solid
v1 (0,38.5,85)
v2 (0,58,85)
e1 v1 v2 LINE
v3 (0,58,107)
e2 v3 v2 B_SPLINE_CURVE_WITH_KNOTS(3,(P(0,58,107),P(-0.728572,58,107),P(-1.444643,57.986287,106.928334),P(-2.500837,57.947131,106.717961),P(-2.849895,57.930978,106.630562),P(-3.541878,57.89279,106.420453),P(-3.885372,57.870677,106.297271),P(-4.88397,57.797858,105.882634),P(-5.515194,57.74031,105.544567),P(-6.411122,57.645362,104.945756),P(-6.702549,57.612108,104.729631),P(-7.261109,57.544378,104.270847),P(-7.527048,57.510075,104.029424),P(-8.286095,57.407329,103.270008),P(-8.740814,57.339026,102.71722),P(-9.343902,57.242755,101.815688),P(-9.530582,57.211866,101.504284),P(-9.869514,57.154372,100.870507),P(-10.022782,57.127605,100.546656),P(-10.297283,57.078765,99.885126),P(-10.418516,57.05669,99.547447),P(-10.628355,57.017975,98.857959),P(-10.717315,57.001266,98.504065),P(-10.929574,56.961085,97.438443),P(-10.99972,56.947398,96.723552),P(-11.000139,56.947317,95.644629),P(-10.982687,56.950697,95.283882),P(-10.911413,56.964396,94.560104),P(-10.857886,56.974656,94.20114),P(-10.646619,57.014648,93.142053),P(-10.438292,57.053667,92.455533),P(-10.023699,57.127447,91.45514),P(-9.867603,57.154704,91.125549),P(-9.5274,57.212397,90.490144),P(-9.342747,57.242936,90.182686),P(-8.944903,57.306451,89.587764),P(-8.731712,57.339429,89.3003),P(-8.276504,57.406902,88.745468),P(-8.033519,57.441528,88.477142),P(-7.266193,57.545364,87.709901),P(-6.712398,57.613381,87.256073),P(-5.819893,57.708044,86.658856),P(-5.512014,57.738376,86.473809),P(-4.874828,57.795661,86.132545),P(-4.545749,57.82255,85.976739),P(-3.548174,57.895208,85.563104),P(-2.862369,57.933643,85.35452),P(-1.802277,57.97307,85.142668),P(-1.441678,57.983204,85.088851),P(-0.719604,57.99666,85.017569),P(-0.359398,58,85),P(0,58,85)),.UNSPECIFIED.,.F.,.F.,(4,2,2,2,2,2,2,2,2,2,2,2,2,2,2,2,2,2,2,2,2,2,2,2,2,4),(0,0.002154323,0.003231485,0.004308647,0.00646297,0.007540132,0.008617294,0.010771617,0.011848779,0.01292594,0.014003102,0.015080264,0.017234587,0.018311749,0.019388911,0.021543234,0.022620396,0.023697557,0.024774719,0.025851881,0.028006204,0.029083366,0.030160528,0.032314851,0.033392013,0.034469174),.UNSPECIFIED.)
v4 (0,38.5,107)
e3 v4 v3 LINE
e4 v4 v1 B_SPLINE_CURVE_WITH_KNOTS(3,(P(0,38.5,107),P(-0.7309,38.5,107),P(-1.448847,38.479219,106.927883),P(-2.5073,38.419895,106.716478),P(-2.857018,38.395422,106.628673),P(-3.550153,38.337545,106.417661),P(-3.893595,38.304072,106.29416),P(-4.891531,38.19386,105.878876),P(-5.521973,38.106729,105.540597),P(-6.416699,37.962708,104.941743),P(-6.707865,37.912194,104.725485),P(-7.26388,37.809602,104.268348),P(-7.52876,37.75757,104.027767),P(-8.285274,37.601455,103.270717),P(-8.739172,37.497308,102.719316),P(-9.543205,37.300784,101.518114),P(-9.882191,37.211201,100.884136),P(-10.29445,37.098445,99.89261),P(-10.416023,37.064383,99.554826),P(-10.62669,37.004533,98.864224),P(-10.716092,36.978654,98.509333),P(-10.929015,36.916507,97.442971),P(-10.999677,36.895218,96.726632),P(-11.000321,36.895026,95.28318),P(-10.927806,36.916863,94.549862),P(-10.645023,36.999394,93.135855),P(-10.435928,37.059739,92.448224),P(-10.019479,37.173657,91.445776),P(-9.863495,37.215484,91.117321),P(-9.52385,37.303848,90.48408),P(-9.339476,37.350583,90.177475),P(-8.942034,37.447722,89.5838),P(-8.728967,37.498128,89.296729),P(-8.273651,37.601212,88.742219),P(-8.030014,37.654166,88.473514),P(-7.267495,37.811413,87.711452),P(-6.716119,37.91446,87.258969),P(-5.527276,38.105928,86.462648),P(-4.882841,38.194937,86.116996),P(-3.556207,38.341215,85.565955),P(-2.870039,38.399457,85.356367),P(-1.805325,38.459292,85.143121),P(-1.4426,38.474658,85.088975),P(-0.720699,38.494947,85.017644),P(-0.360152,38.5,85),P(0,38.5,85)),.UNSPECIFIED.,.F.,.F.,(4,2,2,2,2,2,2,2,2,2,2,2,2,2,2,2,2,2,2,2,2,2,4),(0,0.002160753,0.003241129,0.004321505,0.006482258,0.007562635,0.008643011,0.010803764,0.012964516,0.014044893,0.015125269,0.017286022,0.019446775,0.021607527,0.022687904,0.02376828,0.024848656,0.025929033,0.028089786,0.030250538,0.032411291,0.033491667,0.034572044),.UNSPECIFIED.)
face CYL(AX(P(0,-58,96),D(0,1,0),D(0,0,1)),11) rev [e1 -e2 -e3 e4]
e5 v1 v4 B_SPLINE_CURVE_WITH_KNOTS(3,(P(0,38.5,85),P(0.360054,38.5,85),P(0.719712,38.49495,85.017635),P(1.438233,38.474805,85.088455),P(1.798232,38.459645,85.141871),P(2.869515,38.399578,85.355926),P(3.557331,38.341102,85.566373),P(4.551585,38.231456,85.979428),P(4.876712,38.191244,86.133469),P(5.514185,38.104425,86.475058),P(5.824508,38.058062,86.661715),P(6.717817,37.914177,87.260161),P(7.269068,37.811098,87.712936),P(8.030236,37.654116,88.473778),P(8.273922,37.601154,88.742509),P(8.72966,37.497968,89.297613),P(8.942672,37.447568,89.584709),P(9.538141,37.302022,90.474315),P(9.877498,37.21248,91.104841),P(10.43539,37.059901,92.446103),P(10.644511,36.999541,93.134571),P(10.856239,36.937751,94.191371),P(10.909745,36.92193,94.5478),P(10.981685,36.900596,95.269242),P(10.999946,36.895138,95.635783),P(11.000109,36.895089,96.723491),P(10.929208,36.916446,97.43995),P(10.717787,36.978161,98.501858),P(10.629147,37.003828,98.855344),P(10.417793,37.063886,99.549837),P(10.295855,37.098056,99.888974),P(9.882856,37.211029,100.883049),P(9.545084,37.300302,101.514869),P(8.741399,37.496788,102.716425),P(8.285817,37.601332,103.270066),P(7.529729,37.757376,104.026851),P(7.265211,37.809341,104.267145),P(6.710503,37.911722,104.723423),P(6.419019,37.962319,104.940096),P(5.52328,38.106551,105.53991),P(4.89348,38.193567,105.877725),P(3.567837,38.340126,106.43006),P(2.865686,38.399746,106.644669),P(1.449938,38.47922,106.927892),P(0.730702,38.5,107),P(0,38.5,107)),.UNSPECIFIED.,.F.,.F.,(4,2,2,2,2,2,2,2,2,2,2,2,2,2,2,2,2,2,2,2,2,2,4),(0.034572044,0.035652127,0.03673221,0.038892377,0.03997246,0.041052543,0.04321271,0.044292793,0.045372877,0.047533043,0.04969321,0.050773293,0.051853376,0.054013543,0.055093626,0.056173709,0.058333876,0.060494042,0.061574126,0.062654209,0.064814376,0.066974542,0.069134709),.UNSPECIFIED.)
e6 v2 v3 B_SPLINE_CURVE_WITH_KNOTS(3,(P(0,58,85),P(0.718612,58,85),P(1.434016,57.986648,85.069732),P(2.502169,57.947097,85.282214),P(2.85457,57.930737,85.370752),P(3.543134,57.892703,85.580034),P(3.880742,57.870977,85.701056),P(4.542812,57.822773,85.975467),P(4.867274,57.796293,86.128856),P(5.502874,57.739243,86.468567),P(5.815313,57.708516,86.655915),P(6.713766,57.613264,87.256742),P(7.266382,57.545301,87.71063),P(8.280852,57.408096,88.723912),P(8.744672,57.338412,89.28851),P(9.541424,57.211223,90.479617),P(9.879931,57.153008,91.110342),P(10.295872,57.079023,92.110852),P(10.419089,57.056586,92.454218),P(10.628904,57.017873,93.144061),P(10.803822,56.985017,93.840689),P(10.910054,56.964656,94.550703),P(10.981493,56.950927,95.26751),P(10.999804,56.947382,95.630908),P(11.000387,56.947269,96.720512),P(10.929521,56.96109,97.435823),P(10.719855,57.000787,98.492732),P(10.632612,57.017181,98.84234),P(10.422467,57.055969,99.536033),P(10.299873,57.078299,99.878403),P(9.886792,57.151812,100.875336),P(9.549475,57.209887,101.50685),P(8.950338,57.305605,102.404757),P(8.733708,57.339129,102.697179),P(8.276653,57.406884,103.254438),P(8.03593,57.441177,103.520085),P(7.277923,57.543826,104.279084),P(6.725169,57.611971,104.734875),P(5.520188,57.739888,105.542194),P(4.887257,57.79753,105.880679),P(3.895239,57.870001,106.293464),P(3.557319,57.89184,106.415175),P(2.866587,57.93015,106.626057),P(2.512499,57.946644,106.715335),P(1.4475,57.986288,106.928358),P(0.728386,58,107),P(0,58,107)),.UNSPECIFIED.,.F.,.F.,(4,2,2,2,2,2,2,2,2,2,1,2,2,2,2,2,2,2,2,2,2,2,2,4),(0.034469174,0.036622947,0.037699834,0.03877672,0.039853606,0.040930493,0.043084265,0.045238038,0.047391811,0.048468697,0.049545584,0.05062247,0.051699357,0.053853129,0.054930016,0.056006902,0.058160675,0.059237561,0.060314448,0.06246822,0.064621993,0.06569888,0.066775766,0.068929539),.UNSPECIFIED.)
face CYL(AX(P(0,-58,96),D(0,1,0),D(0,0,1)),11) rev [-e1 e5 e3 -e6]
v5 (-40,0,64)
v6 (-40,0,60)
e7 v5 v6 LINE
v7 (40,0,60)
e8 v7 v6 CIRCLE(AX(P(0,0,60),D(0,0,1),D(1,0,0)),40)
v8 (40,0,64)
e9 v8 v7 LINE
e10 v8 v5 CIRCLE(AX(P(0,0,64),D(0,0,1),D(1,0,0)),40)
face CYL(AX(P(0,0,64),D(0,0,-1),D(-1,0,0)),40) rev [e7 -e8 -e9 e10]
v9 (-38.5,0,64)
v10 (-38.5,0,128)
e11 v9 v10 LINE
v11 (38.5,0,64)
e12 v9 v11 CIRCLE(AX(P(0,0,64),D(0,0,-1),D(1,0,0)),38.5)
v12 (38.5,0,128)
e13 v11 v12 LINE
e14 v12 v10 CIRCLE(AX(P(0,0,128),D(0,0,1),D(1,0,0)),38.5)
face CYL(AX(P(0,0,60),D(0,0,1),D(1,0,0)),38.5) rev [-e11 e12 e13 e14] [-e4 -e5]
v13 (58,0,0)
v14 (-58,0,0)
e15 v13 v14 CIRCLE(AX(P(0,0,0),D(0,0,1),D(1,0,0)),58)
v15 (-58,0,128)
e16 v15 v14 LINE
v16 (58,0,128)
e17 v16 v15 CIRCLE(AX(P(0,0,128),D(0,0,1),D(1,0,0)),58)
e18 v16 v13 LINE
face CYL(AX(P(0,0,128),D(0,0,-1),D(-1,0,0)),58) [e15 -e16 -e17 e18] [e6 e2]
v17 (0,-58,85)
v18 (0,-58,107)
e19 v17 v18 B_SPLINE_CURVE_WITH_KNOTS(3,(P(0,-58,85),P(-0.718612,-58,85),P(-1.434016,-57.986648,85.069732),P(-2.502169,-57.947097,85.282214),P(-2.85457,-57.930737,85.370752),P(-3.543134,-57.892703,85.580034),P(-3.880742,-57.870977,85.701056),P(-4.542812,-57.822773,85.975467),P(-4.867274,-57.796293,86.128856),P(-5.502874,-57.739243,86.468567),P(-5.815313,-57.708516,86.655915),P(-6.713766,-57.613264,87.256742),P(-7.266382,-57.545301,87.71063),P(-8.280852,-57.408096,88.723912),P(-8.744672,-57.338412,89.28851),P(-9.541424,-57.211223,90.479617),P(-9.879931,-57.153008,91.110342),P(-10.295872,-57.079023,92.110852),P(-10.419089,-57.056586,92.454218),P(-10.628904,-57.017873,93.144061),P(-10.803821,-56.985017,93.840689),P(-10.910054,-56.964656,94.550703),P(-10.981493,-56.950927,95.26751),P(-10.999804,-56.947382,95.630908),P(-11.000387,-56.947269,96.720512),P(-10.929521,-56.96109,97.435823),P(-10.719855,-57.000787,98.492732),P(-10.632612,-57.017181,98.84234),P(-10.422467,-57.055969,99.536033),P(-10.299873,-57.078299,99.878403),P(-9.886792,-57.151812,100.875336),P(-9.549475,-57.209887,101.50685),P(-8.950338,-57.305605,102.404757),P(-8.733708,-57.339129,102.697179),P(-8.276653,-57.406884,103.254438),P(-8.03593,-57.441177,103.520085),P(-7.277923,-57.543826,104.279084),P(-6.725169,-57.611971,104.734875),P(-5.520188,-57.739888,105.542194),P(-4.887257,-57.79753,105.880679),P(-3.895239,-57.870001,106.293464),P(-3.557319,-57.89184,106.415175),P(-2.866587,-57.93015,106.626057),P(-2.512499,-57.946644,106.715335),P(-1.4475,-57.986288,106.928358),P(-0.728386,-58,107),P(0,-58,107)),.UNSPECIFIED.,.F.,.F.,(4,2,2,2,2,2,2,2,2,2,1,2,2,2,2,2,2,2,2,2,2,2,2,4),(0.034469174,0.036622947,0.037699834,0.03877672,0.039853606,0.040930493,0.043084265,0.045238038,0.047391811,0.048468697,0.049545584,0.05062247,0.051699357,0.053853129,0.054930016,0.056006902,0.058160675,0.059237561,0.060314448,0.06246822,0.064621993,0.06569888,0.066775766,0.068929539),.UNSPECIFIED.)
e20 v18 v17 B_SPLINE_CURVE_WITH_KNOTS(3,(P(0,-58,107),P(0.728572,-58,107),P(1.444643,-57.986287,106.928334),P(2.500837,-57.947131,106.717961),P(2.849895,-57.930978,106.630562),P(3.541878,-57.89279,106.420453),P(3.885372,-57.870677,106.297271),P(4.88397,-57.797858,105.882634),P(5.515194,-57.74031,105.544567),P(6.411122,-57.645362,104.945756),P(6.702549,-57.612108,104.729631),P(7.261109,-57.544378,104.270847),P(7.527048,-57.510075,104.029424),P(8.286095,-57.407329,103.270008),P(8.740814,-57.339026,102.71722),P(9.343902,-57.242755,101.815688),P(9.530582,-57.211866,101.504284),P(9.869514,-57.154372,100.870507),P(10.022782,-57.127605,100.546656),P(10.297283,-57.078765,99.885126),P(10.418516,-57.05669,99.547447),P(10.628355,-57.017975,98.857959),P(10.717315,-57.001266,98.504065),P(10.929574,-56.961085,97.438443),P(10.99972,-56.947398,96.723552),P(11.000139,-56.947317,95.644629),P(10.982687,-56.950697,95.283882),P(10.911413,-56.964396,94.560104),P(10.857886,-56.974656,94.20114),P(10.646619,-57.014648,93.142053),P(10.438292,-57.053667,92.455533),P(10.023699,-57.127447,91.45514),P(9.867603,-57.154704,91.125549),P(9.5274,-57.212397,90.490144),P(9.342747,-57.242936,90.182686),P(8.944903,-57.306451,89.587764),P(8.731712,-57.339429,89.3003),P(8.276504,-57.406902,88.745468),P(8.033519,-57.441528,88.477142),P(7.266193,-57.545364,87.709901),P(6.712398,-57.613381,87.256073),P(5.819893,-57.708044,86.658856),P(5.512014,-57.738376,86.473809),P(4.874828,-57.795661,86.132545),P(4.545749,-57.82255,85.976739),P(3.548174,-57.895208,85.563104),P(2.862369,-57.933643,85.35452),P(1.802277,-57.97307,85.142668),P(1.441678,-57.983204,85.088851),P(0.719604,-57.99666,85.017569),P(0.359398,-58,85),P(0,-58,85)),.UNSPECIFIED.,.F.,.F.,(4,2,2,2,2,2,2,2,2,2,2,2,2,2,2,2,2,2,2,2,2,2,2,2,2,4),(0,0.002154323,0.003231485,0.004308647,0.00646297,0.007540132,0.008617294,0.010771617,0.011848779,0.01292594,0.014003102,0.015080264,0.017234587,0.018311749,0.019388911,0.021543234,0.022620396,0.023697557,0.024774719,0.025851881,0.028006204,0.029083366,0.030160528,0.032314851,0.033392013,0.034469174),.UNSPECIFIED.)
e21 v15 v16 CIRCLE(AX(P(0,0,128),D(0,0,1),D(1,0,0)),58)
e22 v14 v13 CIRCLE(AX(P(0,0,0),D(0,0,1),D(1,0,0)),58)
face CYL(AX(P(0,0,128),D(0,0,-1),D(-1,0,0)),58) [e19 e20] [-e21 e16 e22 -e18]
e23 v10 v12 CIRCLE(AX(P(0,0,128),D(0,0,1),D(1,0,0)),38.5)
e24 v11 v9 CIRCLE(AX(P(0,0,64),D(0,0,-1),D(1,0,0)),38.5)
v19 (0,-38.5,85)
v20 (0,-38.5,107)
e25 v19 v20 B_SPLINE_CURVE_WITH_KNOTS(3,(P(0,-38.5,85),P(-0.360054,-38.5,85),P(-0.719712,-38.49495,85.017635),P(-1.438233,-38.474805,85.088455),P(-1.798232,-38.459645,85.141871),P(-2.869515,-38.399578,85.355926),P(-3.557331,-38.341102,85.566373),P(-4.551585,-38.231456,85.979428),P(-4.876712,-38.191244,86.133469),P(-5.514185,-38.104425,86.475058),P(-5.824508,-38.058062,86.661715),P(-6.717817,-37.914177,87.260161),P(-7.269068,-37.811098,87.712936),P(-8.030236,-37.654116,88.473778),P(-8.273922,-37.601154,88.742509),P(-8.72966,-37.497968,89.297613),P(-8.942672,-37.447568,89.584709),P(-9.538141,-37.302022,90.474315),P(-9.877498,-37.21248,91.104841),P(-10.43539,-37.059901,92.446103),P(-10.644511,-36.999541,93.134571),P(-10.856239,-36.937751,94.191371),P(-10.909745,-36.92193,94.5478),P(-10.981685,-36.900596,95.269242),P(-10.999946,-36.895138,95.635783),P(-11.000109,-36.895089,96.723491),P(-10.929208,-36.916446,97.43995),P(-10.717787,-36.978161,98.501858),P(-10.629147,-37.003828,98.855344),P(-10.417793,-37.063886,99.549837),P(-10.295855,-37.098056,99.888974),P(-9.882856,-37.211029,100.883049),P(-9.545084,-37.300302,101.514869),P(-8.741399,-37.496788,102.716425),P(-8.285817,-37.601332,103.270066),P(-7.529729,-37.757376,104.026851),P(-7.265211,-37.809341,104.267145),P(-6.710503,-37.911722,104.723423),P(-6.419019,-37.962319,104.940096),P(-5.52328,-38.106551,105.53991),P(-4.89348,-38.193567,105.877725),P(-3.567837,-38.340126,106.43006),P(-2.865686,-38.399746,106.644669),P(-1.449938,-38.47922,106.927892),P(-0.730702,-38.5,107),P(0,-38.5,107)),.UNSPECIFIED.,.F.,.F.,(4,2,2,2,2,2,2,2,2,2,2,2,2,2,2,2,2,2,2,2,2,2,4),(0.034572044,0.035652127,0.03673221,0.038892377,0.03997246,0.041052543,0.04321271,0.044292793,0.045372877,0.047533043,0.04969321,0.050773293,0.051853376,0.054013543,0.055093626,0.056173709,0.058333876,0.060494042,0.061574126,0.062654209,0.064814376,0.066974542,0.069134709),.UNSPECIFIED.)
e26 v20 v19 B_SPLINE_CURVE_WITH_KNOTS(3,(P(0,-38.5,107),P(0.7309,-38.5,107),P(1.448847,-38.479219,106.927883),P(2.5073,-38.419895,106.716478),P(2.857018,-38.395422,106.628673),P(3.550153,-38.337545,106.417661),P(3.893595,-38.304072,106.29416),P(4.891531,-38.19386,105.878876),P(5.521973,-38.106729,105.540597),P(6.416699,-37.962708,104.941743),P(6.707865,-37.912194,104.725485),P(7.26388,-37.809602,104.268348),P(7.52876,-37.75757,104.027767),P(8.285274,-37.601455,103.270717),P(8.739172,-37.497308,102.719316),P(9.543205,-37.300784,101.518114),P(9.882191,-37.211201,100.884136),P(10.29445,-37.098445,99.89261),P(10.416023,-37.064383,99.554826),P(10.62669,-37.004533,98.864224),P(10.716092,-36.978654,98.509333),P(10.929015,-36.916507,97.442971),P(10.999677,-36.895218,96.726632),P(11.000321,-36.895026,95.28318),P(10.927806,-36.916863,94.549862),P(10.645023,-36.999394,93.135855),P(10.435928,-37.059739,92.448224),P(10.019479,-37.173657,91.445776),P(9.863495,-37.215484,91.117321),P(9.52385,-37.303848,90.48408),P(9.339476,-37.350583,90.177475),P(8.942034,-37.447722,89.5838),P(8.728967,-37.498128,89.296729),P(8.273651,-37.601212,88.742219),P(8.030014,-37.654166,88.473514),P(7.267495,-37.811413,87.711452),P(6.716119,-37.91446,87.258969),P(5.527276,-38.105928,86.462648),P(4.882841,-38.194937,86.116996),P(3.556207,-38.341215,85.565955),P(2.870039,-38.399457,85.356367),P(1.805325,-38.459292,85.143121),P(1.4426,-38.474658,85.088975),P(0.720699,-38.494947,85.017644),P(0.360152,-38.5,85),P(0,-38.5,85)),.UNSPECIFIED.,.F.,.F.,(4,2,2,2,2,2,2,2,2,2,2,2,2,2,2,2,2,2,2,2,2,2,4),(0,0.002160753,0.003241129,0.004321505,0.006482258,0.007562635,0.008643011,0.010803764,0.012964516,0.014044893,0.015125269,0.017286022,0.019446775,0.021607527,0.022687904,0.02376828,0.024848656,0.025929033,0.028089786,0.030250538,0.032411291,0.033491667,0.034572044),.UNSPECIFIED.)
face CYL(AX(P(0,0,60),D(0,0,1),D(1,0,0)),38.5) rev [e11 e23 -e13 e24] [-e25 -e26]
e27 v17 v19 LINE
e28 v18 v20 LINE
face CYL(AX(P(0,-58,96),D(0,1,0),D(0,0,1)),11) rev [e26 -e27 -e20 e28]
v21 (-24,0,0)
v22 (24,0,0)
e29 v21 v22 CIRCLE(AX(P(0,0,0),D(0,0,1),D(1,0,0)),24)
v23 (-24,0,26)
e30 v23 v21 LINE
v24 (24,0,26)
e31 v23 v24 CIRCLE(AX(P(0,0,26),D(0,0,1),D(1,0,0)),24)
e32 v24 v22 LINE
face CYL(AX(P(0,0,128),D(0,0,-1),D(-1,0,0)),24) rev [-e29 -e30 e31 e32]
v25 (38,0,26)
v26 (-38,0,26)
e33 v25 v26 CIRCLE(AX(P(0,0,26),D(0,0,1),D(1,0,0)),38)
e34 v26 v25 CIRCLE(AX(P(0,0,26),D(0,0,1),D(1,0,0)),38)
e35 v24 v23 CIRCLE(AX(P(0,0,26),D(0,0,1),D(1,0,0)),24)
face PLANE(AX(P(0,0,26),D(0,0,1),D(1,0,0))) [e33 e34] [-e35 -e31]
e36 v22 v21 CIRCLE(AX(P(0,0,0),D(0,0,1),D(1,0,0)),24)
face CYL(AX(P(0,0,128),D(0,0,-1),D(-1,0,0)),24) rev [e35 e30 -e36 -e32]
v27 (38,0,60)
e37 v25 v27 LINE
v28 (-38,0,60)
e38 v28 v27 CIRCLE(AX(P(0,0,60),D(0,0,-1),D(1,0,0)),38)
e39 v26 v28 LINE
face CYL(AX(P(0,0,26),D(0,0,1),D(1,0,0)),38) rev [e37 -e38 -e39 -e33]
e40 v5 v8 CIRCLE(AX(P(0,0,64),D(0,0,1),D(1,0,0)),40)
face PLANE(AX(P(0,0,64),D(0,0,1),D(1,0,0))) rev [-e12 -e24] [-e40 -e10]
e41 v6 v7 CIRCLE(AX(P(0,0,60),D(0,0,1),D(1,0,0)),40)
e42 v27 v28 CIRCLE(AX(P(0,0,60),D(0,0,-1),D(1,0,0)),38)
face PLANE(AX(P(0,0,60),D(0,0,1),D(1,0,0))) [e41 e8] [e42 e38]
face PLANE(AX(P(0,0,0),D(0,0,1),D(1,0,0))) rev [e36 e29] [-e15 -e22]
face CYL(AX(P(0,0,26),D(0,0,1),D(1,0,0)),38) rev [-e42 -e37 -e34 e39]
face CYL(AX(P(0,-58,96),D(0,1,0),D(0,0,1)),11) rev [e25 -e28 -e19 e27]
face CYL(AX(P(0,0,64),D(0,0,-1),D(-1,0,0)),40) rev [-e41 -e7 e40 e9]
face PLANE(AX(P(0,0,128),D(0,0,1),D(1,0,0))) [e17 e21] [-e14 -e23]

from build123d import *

# Parameters (mm, degrees)
SKETCH1_R               = 58
SKETCH1_R_2             = 24
BOSS_EXTRUDE1_DEPTH     = 128
SKETCH2_R               = 38
CUT_EXTRUDE1_DEPTH      = 102
CUT_EXTRUDE2_DEPTH      = 153.026313512
CUT_EXTRUDE2_DEPTH_BACK = 153.026313512
SKETCH3_R               = 11
SKETCH6_R               = 38.5
CUT_EXTRUDE3_DEPTH      = 68
SKETCH7_R               = 40
CUT_EXTRUDE4_DEPTH      = 4


with BuildPart() as part:
    # Sketch1 → Boss-Extrude1 (new body)
    with BuildSketch(Plane.XY):
        Circle(SKETCH1_R)
        Circle(SKETCH1_R_2, mode=Mode.SUBTRACT)
    extrude(amount=BOSS_EXTRUDE1_DEPTH)

    # Sketch2 → Cut-Extrude1 (cut)
    with BuildSketch(Plane.XY.offset(128)):
        Circle(SKETCH2_R)
    extrude(amount=-CUT_EXTRUDE1_DEPTH, mode=Mode.SUBTRACT)

    # Sketch3 → Cut-Extrude2 (cut, two sides: drawn at the far end of the back side and taken through both)
    with BuildSketch(Plane(origin=(0, 0, 0), x_dir=(1, 0, 0), z_dir=(0, 1, 0)).offset(-CUT_EXTRUDE2_DEPTH_BACK)):
        with Locations(Location((0, -96, 0), (0, 0, 270))):
            Circle(SKETCH3_R)
    extrude(amount=CUT_EXTRUDE2_DEPTH + CUT_EXTRUDE2_DEPTH_BACK, mode=Mode.SUBTRACT)

    # Sketch6 → Cut-Extrude3 (cut)
    with BuildSketch(Plane.XY.offset(128)):
        Circle(SKETCH6_R)
    extrude(amount=-CUT_EXTRUDE3_DEPTH, mode=Mode.SUBTRACT)

    # Sketch7 → Cut-Extrude4 (cut)
    with BuildSketch(Plane.XY.offset(60)):
        Circle(SKETCH7_R)
    extrude(amount=CUT_EXTRUDE4_DEPTH, mode=Mode.SUBTRACT)


solid = part.part
